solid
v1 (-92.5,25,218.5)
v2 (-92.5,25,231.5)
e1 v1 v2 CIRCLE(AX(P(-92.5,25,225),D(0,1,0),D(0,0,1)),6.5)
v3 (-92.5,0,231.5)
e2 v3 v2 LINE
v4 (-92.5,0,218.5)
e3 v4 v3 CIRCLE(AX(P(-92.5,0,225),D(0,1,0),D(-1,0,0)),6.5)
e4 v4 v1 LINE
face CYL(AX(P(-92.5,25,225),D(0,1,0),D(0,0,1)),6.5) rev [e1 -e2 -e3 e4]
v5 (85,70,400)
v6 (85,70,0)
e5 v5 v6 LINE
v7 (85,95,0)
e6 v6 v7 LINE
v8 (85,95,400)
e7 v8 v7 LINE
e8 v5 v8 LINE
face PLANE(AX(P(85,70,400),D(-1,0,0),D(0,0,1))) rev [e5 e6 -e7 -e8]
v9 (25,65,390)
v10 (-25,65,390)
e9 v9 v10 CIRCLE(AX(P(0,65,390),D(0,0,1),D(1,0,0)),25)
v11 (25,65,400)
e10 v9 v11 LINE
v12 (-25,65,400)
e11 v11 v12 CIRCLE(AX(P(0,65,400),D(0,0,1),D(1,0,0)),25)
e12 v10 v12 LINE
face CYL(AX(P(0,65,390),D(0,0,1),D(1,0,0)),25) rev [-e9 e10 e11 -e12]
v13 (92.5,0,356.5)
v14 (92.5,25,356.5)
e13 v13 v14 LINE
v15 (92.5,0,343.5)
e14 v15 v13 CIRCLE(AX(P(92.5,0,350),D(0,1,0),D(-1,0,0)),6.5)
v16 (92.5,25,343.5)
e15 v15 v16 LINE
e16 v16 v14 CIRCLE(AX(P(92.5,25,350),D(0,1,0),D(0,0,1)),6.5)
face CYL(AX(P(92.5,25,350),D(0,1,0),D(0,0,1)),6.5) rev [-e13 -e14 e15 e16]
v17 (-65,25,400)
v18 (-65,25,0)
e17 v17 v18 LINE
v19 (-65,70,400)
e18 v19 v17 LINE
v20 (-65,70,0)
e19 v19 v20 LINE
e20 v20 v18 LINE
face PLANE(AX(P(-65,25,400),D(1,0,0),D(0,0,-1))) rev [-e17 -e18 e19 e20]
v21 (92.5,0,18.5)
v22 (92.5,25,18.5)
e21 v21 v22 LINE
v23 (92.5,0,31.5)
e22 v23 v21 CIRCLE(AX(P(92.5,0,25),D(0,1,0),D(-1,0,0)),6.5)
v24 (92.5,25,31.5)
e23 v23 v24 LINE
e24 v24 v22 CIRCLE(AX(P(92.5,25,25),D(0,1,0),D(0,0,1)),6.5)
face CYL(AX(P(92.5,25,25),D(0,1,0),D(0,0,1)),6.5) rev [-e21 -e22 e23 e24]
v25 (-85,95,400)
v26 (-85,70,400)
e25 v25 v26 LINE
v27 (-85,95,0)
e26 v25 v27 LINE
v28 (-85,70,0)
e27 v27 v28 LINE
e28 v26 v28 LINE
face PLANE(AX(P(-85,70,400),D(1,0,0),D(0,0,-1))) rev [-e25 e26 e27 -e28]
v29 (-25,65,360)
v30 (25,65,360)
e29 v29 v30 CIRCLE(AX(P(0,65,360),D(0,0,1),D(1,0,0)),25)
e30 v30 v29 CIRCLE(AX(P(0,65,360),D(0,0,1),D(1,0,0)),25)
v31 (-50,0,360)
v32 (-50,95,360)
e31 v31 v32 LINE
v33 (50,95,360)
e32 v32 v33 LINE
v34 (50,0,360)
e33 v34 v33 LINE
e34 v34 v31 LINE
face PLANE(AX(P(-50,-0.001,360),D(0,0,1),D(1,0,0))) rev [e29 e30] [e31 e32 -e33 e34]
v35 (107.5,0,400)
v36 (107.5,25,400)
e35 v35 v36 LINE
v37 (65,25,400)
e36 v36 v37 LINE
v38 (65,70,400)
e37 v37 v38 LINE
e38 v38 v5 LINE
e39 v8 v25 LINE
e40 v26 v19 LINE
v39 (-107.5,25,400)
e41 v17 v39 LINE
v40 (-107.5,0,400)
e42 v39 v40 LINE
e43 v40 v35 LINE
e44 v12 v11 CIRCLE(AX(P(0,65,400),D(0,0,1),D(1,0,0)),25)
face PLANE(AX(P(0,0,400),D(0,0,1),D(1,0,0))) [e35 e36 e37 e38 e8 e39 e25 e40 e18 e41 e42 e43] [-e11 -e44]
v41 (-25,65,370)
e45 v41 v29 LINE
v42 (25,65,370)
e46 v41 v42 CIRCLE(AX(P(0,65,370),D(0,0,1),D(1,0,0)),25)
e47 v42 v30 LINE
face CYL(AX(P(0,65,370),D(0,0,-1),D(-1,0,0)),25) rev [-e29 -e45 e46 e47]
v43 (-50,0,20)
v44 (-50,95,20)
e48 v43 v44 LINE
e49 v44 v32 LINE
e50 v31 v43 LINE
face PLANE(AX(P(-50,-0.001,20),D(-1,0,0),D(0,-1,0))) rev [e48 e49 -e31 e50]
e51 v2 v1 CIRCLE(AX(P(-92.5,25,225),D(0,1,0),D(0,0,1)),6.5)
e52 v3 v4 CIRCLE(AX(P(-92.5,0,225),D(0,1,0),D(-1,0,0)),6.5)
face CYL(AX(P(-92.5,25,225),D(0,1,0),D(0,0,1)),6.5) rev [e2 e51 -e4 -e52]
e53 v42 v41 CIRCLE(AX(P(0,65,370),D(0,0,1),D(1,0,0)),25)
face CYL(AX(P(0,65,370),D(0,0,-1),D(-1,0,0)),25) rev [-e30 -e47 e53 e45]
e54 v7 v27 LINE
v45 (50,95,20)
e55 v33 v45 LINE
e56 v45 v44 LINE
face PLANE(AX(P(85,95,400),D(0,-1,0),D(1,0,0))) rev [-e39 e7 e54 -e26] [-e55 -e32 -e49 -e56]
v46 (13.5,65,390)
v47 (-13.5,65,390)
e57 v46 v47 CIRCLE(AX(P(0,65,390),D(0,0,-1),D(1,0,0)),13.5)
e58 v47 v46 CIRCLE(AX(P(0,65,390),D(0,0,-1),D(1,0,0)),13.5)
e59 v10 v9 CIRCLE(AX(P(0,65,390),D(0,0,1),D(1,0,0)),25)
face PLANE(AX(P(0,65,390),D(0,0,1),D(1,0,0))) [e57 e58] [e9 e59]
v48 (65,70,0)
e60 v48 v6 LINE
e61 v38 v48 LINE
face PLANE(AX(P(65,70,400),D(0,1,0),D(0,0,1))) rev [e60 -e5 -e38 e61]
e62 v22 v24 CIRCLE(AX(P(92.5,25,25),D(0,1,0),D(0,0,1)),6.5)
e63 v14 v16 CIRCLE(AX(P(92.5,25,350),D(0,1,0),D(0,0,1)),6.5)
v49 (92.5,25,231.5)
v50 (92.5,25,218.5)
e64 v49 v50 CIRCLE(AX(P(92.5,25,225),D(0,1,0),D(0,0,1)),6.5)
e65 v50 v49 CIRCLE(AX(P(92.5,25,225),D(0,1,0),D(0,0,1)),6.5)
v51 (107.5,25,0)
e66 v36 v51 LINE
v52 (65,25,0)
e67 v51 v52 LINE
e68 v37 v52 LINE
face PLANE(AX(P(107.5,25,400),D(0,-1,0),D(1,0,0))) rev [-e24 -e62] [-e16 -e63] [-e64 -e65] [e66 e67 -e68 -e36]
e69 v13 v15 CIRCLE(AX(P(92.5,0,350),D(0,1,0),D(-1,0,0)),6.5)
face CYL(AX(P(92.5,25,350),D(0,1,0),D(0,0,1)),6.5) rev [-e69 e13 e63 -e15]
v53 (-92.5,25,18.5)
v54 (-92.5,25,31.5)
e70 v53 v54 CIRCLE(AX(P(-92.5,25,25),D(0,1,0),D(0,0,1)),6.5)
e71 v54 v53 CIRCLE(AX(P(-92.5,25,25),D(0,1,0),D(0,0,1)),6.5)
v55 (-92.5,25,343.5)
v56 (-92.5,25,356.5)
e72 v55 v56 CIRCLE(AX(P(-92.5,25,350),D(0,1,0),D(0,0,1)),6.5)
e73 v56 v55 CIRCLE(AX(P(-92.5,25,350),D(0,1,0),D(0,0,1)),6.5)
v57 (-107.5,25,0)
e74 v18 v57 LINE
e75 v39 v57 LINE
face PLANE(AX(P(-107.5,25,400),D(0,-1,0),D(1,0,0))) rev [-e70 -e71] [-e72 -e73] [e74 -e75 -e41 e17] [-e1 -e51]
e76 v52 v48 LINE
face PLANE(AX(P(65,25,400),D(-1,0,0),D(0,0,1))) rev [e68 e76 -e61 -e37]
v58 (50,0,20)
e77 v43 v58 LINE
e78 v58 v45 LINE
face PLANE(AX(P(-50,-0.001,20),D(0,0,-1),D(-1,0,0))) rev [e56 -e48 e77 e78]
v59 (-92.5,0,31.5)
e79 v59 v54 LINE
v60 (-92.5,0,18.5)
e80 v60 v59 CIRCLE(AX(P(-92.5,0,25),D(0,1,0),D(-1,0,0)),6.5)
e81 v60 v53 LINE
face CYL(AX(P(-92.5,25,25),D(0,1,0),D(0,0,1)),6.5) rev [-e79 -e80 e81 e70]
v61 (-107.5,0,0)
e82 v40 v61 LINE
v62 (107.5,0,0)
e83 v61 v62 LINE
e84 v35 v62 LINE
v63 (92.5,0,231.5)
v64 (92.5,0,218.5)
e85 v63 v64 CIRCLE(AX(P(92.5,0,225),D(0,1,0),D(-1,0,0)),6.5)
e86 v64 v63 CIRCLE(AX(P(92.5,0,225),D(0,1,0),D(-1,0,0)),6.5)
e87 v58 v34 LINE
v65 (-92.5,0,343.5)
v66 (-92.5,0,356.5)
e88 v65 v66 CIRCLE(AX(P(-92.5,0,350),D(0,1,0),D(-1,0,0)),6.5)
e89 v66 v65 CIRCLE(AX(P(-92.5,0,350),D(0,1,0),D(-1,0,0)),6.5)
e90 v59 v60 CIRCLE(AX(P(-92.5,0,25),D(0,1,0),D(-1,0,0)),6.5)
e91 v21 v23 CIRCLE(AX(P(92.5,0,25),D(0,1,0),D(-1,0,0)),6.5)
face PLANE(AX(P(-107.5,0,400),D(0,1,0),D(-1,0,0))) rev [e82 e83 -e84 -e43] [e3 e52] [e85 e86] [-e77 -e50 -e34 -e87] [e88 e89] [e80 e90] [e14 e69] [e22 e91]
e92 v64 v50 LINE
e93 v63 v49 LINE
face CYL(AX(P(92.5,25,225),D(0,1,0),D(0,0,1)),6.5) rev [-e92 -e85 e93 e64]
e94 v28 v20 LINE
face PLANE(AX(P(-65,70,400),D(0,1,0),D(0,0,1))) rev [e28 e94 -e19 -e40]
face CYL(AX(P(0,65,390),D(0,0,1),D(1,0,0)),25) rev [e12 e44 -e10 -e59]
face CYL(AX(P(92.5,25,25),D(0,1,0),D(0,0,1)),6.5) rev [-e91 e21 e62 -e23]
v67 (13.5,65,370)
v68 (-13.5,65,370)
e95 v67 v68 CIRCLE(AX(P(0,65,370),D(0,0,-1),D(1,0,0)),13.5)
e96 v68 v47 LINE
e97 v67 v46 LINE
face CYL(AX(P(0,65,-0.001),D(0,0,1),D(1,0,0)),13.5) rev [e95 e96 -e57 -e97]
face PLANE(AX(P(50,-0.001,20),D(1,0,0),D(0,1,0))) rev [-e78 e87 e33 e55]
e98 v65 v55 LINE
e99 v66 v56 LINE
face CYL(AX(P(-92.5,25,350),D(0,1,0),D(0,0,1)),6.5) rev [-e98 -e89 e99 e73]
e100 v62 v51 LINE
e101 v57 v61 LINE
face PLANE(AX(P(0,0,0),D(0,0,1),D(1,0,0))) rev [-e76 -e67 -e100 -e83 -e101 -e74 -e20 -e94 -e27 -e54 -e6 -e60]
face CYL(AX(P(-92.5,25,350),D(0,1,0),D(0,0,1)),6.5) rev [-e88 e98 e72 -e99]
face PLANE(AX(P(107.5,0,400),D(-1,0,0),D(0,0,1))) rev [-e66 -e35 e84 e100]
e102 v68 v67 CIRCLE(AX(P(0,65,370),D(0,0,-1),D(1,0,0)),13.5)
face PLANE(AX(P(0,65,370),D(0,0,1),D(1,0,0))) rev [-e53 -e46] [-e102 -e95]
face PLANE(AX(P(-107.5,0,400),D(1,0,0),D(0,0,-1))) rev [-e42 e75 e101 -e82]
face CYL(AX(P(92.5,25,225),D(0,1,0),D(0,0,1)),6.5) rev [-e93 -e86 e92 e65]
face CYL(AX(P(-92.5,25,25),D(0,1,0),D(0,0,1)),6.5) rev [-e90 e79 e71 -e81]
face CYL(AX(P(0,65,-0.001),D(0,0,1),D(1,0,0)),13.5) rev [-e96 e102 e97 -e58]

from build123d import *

# Parameters (mm, degrees)
EXTRUDE_1_DEPTH             = 400
CUT_EXTRUDE_1_REACH         = 426.949
SKETCH_2_W                  = 100
SKETCH_2_H                  = 340
CUT_EXTRUDE_2_REACH         = 426.949
SKETCH_3_R                  = 13.5
SKETCH_4_R                  = 25
CUT_EXTRUDE_3_DEPTH         = 10
CUT_EXTRUDE_START           = -30
SKETCH_4_2_R                = 25
CUT_EXTRUDE_4_DEPTH         = 10
HOLE_WIZARD_13_0_13_1_D     = 13
HOLE_WIZARD_13_0_13_1_DEPTH = 70
HOLE_WIZARD_13_0_13_1_TIP   = 3.905594024


with BuildPart() as part:
    # 草图1 → 凸台-拉伸1 (new body)
    with BuildSketch(Plane.XY):
        Polygon((-107.5, 0), (107.5, 0), (107.5, 25), (65, 25), (65, 70), (85, 70), (85, 95), (-85, 95), (-85, 70), (-65, 70), (-65, 25), (-107.5, 25), align=None)
    extrude(amount=EXTRUDE_1_DEPTH)

    # 草图2 → 切除-拉伸1 (cut, up to next)
    with BuildSketch(Plane(origin=(0, 95, 0), x_dir=(1, 0, 0), z_dir=(0, 1, 0)), mode=Mode.PRIVATE) as cut_extrude_1_sk1:
        with Locations((0, -190)):
            Rectangle(SKETCH_2_W, SKETCH_2_H)
    cut_extrude_1_tool1 = extrude(cut_extrude_1_sk1.sketch, amount=-CUT_EXTRUDE_1_REACH, mode=Mode.PRIVATE) & part.part
    add(cut_extrude_1_tool1.solids().sort_by_distance((0, 95, 190))[0], mode=Mode.SUBTRACT)

    # 草图3 → 切除-拉伸2 (cut, up to next)
    with BuildSketch(Plane.XY.offset(400), mode=Mode.PRIVATE) as cut_extrude_2_sk1:
        with Locations((0, 65)):
            Circle(SKETCH_3_R)
    cut_extrude_2_tool1 = extrude(cut_extrude_2_sk1.sketch, amount=-CUT_EXTRUDE_2_REACH, mode=Mode.PRIVATE) & part.part
    add(cut_extrude_2_tool1.solids().sort_by_distance((0, 65, 400))[0], mode=Mode.SUBTRACT)

    # 草图4 → 切除-拉伸3 (cut)
    with BuildSketch(Plane.XY.offset(400)):
        with Locations((0, 65)):
            Circle(SKETCH_4_R)
    extrude(amount=-CUT_EXTRUDE_3_DEPTH, mode=Mode.SUBTRACT)

    # 草图4<2> → 切除-拉伸4 (cut)
    with BuildSketch(Plane.XY.offset(400).offset(CUT_EXTRUDE_START)):
        with Locations((0, 65)):
            Circle(SKETCH_4_2_R)
    extrude(amount=-CUT_EXTRUDE_4_DEPTH, mode=Mode.SUBTRACT)

    # Ø13.0 (13) 直径孔1
    with Locations(Plane(origin=(0, 25, 0), x_dir=(1, 0, 0), z_dir=(0, 1, 0))):
        with Locations((-92.5, -350), (92.5, -350), (-92.5, -225), (92.5, -225), (-92.5, -25), (92.5, -25)):
            Hole(HOLE_WIZARD_13_0_13_1_D / 2, depth=HOLE_WIZARD_13_0_13_1_DEPTH)
            with Locations((0, 0, -(HOLE_WIZARD_13_0_13_1_DEPTH + HOLE_WIZARD_13_0_13_1_TIP / 2))):  # 118° drill point
                Cone(0, HOLE_WIZARD_13_0_13_1_D / 2, HOLE_WIZARD_13_0_13_1_TIP, mode=Mode.SUBTRACT)


solid = part.part
